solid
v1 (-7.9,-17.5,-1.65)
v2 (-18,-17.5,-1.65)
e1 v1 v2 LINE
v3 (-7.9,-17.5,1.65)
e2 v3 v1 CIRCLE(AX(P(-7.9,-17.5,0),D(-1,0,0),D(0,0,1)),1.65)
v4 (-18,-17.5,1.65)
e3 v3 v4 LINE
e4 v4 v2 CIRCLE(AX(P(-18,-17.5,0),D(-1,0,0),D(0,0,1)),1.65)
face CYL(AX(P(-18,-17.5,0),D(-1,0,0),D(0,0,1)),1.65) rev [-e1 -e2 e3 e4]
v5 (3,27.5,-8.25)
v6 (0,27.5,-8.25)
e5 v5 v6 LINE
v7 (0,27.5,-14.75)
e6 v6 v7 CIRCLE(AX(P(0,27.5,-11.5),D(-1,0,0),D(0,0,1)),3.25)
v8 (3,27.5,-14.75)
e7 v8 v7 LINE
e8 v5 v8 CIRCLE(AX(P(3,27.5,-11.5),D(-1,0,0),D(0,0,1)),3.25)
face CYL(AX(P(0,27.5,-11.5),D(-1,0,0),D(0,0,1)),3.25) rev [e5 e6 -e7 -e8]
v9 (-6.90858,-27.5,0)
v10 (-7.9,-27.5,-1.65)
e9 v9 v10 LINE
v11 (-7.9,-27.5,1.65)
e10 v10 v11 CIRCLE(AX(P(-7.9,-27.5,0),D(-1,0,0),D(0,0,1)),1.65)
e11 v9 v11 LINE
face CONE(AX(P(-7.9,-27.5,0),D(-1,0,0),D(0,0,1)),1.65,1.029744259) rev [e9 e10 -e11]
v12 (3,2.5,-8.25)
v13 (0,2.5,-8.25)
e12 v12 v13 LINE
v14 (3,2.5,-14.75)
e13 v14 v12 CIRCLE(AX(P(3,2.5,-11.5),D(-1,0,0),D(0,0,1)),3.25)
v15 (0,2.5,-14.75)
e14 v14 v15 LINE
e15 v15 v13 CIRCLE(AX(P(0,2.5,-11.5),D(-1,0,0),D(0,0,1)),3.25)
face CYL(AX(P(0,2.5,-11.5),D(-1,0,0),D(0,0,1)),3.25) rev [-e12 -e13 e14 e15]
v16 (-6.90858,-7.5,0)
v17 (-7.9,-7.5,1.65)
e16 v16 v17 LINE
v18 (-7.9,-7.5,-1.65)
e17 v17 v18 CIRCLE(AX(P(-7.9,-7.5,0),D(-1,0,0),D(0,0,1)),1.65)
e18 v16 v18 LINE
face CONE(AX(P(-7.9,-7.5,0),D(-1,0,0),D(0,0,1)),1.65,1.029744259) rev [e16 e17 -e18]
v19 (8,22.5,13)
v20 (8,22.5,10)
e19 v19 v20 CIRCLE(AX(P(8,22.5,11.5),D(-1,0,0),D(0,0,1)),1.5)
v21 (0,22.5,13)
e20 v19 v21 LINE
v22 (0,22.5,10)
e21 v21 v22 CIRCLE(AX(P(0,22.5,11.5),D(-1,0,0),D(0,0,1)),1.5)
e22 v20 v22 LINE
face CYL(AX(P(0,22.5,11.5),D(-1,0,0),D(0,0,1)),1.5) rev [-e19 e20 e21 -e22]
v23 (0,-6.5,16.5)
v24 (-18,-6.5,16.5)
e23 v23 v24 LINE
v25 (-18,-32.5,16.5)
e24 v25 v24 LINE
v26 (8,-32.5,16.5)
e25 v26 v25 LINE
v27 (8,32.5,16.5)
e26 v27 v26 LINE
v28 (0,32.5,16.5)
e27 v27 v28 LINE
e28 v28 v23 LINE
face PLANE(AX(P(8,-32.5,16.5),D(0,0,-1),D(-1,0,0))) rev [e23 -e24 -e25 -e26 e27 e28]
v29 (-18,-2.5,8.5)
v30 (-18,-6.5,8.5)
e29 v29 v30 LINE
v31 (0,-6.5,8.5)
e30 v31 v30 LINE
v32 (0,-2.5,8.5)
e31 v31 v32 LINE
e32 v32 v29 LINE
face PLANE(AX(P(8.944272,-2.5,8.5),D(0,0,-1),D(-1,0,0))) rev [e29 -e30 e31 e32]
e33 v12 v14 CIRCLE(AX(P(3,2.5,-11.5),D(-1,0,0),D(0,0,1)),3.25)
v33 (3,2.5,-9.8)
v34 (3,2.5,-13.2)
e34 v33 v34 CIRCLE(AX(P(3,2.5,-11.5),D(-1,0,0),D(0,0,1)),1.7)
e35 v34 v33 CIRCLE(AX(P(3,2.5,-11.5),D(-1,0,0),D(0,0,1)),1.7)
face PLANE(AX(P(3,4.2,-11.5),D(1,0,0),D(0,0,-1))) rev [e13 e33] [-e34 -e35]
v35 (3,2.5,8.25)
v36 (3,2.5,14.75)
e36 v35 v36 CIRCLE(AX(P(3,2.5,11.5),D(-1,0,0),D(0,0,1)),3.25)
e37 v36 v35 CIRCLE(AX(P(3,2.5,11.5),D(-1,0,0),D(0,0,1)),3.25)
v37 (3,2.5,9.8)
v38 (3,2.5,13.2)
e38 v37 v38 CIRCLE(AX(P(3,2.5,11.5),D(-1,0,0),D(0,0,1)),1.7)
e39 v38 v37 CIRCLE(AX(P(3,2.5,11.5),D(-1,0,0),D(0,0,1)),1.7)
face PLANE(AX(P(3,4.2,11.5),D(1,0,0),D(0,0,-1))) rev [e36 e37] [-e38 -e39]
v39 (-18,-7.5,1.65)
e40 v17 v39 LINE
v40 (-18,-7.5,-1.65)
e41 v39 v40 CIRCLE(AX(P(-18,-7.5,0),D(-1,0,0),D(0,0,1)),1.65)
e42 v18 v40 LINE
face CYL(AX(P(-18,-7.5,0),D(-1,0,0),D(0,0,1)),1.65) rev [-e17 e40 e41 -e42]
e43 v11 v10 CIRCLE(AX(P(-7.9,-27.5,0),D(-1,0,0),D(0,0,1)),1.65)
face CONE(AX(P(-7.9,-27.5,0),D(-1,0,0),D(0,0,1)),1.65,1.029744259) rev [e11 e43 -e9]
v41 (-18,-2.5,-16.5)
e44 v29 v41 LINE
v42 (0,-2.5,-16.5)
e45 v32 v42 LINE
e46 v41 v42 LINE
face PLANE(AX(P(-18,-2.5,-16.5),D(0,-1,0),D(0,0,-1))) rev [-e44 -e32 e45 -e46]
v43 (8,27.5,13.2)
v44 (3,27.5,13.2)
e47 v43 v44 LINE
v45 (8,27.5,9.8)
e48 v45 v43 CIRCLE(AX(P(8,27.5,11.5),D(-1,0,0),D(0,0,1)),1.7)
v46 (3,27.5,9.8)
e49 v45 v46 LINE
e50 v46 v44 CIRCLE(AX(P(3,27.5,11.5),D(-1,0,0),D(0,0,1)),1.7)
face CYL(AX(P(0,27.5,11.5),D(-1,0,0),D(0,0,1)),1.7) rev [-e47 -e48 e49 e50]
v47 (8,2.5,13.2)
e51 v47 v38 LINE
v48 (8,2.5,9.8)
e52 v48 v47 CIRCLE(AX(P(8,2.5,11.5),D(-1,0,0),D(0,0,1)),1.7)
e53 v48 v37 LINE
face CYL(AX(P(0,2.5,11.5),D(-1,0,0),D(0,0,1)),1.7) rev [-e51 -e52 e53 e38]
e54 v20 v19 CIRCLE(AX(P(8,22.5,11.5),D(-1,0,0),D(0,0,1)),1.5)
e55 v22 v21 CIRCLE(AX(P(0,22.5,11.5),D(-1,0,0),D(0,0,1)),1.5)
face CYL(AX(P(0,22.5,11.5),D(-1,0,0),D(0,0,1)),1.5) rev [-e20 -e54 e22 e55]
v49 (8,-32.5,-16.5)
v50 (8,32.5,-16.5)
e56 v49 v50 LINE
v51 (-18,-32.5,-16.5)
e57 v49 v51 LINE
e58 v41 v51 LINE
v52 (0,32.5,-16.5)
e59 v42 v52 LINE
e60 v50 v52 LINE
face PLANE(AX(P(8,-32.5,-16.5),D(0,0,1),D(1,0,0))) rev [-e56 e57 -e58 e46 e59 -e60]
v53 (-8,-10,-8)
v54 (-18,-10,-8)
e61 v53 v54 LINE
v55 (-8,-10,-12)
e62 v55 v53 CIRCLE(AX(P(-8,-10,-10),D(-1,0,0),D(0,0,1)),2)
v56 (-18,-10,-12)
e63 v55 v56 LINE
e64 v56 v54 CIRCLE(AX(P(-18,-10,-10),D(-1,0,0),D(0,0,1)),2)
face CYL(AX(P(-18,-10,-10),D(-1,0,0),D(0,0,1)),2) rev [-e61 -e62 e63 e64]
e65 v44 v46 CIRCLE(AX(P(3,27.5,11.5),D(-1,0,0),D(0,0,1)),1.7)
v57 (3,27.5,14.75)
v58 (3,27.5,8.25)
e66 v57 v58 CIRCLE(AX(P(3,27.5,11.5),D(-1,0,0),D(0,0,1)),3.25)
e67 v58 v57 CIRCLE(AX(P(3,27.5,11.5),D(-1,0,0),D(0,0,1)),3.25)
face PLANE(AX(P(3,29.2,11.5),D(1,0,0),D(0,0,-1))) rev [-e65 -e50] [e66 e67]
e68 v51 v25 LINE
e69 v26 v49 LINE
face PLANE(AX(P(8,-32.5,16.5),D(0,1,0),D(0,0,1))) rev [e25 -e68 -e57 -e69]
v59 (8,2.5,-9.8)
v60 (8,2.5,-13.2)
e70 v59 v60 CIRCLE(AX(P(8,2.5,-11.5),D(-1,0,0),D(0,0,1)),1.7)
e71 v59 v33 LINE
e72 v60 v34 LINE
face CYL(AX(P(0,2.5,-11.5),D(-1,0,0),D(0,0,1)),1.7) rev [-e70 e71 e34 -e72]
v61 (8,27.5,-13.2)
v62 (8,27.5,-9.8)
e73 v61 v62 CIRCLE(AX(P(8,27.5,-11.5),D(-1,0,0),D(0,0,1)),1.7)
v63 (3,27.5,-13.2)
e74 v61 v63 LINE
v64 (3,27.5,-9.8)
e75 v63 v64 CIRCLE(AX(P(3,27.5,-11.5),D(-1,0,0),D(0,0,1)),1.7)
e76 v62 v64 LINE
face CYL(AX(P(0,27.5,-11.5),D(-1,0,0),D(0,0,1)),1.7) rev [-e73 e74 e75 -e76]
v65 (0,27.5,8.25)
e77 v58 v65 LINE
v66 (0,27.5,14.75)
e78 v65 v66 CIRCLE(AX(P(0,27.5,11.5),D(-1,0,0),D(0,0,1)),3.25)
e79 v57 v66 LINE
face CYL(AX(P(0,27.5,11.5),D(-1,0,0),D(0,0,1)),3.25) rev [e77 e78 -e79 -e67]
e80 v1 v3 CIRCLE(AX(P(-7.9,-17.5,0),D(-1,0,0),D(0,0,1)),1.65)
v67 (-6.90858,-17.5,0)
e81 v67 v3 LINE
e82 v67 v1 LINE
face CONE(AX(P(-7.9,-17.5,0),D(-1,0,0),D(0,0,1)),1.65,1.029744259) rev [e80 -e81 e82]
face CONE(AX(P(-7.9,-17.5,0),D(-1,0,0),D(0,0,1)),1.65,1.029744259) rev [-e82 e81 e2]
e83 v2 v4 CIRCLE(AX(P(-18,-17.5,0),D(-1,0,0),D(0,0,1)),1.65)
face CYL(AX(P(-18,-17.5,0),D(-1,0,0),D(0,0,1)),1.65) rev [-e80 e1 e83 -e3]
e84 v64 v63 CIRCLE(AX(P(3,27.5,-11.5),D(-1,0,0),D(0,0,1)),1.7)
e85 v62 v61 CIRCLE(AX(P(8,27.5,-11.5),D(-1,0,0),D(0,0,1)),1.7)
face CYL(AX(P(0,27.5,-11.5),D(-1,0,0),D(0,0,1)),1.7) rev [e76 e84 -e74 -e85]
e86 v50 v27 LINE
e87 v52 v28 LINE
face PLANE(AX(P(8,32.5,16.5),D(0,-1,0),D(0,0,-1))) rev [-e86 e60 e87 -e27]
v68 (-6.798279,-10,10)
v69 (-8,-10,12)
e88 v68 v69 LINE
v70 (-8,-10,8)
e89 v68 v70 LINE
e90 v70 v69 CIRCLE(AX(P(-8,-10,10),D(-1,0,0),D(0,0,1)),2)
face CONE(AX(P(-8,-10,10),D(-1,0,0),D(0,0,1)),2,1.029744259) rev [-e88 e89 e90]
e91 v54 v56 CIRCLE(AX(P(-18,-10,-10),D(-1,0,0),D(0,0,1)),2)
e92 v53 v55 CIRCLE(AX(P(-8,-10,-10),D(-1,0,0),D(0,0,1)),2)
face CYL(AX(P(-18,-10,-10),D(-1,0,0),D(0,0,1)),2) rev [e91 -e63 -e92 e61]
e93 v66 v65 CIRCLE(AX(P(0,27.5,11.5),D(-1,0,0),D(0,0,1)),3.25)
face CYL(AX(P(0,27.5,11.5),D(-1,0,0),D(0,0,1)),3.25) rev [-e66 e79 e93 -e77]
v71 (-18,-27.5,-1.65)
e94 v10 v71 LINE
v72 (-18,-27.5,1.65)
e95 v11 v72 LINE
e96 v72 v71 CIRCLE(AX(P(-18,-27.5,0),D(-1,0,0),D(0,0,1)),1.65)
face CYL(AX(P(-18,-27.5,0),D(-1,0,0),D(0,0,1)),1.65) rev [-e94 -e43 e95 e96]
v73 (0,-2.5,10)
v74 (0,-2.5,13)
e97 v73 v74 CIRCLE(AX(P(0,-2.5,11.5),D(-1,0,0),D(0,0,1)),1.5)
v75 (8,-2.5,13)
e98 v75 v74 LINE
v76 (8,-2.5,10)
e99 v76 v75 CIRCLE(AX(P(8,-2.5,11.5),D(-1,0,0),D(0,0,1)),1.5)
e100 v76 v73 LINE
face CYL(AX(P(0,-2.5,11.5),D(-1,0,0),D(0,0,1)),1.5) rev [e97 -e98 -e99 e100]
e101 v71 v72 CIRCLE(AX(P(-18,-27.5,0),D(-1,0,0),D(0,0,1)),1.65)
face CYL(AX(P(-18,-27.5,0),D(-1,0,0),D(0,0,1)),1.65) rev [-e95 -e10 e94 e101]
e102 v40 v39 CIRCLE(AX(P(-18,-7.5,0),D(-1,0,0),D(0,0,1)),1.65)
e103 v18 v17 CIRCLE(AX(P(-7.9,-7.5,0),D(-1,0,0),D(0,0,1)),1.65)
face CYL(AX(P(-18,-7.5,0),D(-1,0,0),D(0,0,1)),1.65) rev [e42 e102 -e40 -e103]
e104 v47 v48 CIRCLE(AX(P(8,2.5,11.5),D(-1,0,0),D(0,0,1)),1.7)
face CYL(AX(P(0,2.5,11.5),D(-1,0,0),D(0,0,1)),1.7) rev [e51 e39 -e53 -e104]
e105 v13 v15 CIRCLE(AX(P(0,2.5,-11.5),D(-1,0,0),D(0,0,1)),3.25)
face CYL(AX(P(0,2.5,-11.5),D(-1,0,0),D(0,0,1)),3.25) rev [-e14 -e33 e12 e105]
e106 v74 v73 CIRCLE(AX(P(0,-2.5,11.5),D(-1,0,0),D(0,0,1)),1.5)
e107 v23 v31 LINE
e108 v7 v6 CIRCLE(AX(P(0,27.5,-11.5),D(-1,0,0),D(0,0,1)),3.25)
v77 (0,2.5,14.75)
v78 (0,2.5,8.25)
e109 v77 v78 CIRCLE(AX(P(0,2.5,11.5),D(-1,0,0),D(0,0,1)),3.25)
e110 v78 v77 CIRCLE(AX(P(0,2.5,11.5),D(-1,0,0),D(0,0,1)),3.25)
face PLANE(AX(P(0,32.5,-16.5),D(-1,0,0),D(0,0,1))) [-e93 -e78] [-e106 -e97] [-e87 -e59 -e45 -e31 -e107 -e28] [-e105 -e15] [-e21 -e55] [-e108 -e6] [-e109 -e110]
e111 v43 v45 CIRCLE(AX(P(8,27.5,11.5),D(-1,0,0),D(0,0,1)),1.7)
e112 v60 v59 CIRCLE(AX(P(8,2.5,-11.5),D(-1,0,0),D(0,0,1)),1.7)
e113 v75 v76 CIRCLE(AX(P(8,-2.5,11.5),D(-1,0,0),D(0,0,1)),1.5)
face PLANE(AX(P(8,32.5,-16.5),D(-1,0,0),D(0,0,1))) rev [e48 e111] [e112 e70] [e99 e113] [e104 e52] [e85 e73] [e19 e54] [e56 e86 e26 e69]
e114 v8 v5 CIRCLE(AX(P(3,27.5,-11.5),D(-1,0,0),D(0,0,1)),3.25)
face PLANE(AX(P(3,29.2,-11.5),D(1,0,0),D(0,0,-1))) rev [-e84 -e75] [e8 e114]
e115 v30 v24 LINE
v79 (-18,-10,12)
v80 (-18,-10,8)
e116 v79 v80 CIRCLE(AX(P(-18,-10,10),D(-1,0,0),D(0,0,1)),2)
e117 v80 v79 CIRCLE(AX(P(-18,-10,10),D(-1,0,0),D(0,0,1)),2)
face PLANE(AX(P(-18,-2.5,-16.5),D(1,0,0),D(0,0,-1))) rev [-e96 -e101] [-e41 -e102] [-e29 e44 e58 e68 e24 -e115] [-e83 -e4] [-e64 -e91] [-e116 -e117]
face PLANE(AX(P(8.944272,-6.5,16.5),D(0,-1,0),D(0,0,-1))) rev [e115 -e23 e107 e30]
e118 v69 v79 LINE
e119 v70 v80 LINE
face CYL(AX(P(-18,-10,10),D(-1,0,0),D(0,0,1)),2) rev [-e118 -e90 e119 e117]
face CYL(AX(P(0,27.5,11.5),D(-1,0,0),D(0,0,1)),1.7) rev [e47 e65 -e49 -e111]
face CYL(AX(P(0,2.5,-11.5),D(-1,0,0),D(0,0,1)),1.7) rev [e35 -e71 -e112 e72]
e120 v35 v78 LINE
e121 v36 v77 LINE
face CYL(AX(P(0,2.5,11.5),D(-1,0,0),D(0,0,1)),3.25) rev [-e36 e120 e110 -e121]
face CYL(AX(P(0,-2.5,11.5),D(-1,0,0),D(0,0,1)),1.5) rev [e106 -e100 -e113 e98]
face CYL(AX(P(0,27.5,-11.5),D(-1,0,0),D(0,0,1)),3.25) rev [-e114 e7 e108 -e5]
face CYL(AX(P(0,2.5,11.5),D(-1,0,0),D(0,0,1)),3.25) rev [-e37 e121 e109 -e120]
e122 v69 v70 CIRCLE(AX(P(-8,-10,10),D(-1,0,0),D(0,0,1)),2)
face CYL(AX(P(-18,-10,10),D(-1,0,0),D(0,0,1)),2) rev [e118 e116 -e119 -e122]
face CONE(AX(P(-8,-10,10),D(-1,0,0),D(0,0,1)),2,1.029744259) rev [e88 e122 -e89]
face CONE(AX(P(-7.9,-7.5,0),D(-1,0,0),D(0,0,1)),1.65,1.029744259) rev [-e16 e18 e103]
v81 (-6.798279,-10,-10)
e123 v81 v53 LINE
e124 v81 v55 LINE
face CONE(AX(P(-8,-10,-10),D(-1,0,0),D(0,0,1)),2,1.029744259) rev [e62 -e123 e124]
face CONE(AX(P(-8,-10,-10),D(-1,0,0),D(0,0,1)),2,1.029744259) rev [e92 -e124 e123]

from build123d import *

# Parameters (mm, degrees)
SKETCH_1_W                                        = 33
SKETCH_1_H                                        = 65
BOSS_EXTRUDE_1_DEPTH                              = 8
SKETCH_2_W                                        = 33
SKETCH_2_H                                        = 30
BOSS_EXTRUDE_2_DEPTH                              = 18
M3_HEX_SOCKET_CAP_SCREW_COUNTERBORE_1_D           = 3.4
M3_HEX_SOCKET_CAP_SCREW_COUNTERBORE_1_CBORE_D     = 6.5
M3_HEX_SOCKET_CAP_SCREW_COUNTERBORE_1_CBORE_DEPTH = 3
LINEAR_PATTERN_1_COUNT                            = 2
LINEAR_PATTERN_1_PITCH                            = 23
LINEAR_PATTERN_1_COUNT_DIR2                       = 2
LINEAR_PATTERN_1_PITCH_DIR2                       = 25
LINEAR_PATTERN_3_COUNT                            = 3
LINEAR_PATTERN_3_PITCH                            = 10
SKETCH_9_W                                        = 1.5
SKETCH_9_H                                        = 8
LINEAR_PATTERN_4_COUNT                            = 2
LINEAR_PATTERN_4_PITCH                            = 25
SKETCH_11_W                                       = 8
SKETCH_11_H                                       = 4
CUT_EXTRUDE_1_DEPTH                               = 18
LINEAR_PATTERN_5_COUNT                            = 2
LINEAR_PATTERN_5_PITCH                            = 20


with BuildPart() as part:
    # Sketch 1 → Boss-Extrude 1 (new body)
    with BuildSketch(Plane(origin=(0, 0, 0), x_dir=(0, 0, -1), z_dir=(1, 0, 0))):
        Rectangle(SKETCH_1_W, SKETCH_1_H)
    extrude(amount=BOSS_EXTRUDE_1_DEPTH)

    # Sketch 2 → Boss-Extrude 2 (add)
    with BuildSketch(Plane.ZY):
        with Locations((0, -17.5)):
            Rectangle(SKETCH_2_W, SKETCH_2_H)
    extrude(amount=BOSS_EXTRUDE_2_DEPTH)

    # M3 Hex Socket Cap Screw Counterbore 1 (through all)
    with Locations(Plane.ZY):
        with Locations((-11.5, 27.5)):
            m3_hex_socket_cap_screw_counterbore_1 = CounterBoreHole(M3_HEX_SOCKET_CAP_SCREW_COUNTERBORE_1_D / 2, M3_HEX_SOCKET_CAP_SCREW_COUNTERBORE_1_CBORE_D / 2, M3_HEX_SOCKET_CAP_SCREW_COUNTERBORE_1_CBORE_DEPTH)

    # Linear Pattern 1: M3 Hex Socket Cap Screw Counterbore 1 2 × 2
    with Locations(*[(0, -j * LINEAR_PATTERN_1_PITCH_DIR2, i * LINEAR_PATTERN_1_PITCH) for i in range(LINEAR_PATTERN_1_COUNT) for j in range(LINEAR_PATTERN_1_COUNT_DIR2) if (i, j) != (0, 0)]):
        add(m3_hex_socket_cap_screw_counterbore_1, mode=Mode.SUBTRACT)

    # Sketch 7 → M4 Tapped Hole 2 (revolve, cut)
    with BuildSketch(Plane(origin=(-18, -27.5, 0), x_dir=(0, 0, 1), z_dir=(0, 1, 0))):
        Polygon((0, 0), (0, 11.091420021), (1.65, 10.1), (1.65, 0), align=None)
    m4_tapped_hole_2 = revolve(axis=Axis((-24.35, -27.5, 0), (1, 0, 0)), mode=Mode.SUBTRACT)

    # Linear Pattern 3: M4 Tapped Hole 2 ×3
    with Locations(*[(0, i * LINEAR_PATTERN_3_PITCH, 0) for i in range(1, LINEAR_PATTERN_3_COUNT)]):
        add(m4_tapped_hole_2, mode=Mode.SUBTRACT)

    # Sketch 9 → Ø3.0 (3) Hole 1 (revolve, cut)
    with BuildSketch(Plane(origin=(0, 22.5, 11.5), x_dir=(0, 0, 1), z_dir=(0, 1, 0))):
        with Locations((0.75, 4)):
            Rectangle(SKETCH_9_W, SKETCH_9_H)
    f_3_0_3_hole_1 = revolve(axis=Axis((-6.35, 22.5, 11.5), (1, 0, 0)), mode=Mode.SUBTRACT)

    # Linear Pattern 4: Ø3.0 (3) Hole 1 ×2
    with Locations(*[(0, -i * LINEAR_PATTERN_4_PITCH, 0) for i in range(1, LINEAR_PATTERN_4_COUNT)]):
        add(f_3_0_3_hole_1, mode=Mode.SUBTRACT)

    # Sketch 11 → Cut-Extrude 1 (cut)
    with BuildSketch(Plane.ZY.offset(18)):
        with Locations((12.5, -4.5)):
            Rectangle(SKETCH_11_W, SKETCH_11_H)
    extrude(amount=-CUT_EXTRUDE_1_DEPTH, mode=Mode.SUBTRACT)

    # Sketch 12 → Ø4.0 (4) Hole 1 (revolve, cut)
    with BuildSketch(Plane(origin=(-18, -10, -10), x_dir=(0, 0, 1), z_dir=(0, 1, 0))):
        Polygon((0, 0), (0, 11.201721238), (2, 10), (2, 0), align=None)
    f_4_0_4_hole_1 = revolve(axis=Axis((-24.35, -10, -10), (1, 0, 0)), mode=Mode.SUBTRACT)

    # Linear Pattern 5: Ø4.0 (4) Hole 1 ×2
    with Locations(*[(0, 0, i * LINEAR_PATTERN_5_PITCH) for i in range(1, LINEAR_PATTERN_5_COUNT)]):
        add(f_4_0_4_hole_1, mode=Mode.SUBTRACT)


solid = part.part
